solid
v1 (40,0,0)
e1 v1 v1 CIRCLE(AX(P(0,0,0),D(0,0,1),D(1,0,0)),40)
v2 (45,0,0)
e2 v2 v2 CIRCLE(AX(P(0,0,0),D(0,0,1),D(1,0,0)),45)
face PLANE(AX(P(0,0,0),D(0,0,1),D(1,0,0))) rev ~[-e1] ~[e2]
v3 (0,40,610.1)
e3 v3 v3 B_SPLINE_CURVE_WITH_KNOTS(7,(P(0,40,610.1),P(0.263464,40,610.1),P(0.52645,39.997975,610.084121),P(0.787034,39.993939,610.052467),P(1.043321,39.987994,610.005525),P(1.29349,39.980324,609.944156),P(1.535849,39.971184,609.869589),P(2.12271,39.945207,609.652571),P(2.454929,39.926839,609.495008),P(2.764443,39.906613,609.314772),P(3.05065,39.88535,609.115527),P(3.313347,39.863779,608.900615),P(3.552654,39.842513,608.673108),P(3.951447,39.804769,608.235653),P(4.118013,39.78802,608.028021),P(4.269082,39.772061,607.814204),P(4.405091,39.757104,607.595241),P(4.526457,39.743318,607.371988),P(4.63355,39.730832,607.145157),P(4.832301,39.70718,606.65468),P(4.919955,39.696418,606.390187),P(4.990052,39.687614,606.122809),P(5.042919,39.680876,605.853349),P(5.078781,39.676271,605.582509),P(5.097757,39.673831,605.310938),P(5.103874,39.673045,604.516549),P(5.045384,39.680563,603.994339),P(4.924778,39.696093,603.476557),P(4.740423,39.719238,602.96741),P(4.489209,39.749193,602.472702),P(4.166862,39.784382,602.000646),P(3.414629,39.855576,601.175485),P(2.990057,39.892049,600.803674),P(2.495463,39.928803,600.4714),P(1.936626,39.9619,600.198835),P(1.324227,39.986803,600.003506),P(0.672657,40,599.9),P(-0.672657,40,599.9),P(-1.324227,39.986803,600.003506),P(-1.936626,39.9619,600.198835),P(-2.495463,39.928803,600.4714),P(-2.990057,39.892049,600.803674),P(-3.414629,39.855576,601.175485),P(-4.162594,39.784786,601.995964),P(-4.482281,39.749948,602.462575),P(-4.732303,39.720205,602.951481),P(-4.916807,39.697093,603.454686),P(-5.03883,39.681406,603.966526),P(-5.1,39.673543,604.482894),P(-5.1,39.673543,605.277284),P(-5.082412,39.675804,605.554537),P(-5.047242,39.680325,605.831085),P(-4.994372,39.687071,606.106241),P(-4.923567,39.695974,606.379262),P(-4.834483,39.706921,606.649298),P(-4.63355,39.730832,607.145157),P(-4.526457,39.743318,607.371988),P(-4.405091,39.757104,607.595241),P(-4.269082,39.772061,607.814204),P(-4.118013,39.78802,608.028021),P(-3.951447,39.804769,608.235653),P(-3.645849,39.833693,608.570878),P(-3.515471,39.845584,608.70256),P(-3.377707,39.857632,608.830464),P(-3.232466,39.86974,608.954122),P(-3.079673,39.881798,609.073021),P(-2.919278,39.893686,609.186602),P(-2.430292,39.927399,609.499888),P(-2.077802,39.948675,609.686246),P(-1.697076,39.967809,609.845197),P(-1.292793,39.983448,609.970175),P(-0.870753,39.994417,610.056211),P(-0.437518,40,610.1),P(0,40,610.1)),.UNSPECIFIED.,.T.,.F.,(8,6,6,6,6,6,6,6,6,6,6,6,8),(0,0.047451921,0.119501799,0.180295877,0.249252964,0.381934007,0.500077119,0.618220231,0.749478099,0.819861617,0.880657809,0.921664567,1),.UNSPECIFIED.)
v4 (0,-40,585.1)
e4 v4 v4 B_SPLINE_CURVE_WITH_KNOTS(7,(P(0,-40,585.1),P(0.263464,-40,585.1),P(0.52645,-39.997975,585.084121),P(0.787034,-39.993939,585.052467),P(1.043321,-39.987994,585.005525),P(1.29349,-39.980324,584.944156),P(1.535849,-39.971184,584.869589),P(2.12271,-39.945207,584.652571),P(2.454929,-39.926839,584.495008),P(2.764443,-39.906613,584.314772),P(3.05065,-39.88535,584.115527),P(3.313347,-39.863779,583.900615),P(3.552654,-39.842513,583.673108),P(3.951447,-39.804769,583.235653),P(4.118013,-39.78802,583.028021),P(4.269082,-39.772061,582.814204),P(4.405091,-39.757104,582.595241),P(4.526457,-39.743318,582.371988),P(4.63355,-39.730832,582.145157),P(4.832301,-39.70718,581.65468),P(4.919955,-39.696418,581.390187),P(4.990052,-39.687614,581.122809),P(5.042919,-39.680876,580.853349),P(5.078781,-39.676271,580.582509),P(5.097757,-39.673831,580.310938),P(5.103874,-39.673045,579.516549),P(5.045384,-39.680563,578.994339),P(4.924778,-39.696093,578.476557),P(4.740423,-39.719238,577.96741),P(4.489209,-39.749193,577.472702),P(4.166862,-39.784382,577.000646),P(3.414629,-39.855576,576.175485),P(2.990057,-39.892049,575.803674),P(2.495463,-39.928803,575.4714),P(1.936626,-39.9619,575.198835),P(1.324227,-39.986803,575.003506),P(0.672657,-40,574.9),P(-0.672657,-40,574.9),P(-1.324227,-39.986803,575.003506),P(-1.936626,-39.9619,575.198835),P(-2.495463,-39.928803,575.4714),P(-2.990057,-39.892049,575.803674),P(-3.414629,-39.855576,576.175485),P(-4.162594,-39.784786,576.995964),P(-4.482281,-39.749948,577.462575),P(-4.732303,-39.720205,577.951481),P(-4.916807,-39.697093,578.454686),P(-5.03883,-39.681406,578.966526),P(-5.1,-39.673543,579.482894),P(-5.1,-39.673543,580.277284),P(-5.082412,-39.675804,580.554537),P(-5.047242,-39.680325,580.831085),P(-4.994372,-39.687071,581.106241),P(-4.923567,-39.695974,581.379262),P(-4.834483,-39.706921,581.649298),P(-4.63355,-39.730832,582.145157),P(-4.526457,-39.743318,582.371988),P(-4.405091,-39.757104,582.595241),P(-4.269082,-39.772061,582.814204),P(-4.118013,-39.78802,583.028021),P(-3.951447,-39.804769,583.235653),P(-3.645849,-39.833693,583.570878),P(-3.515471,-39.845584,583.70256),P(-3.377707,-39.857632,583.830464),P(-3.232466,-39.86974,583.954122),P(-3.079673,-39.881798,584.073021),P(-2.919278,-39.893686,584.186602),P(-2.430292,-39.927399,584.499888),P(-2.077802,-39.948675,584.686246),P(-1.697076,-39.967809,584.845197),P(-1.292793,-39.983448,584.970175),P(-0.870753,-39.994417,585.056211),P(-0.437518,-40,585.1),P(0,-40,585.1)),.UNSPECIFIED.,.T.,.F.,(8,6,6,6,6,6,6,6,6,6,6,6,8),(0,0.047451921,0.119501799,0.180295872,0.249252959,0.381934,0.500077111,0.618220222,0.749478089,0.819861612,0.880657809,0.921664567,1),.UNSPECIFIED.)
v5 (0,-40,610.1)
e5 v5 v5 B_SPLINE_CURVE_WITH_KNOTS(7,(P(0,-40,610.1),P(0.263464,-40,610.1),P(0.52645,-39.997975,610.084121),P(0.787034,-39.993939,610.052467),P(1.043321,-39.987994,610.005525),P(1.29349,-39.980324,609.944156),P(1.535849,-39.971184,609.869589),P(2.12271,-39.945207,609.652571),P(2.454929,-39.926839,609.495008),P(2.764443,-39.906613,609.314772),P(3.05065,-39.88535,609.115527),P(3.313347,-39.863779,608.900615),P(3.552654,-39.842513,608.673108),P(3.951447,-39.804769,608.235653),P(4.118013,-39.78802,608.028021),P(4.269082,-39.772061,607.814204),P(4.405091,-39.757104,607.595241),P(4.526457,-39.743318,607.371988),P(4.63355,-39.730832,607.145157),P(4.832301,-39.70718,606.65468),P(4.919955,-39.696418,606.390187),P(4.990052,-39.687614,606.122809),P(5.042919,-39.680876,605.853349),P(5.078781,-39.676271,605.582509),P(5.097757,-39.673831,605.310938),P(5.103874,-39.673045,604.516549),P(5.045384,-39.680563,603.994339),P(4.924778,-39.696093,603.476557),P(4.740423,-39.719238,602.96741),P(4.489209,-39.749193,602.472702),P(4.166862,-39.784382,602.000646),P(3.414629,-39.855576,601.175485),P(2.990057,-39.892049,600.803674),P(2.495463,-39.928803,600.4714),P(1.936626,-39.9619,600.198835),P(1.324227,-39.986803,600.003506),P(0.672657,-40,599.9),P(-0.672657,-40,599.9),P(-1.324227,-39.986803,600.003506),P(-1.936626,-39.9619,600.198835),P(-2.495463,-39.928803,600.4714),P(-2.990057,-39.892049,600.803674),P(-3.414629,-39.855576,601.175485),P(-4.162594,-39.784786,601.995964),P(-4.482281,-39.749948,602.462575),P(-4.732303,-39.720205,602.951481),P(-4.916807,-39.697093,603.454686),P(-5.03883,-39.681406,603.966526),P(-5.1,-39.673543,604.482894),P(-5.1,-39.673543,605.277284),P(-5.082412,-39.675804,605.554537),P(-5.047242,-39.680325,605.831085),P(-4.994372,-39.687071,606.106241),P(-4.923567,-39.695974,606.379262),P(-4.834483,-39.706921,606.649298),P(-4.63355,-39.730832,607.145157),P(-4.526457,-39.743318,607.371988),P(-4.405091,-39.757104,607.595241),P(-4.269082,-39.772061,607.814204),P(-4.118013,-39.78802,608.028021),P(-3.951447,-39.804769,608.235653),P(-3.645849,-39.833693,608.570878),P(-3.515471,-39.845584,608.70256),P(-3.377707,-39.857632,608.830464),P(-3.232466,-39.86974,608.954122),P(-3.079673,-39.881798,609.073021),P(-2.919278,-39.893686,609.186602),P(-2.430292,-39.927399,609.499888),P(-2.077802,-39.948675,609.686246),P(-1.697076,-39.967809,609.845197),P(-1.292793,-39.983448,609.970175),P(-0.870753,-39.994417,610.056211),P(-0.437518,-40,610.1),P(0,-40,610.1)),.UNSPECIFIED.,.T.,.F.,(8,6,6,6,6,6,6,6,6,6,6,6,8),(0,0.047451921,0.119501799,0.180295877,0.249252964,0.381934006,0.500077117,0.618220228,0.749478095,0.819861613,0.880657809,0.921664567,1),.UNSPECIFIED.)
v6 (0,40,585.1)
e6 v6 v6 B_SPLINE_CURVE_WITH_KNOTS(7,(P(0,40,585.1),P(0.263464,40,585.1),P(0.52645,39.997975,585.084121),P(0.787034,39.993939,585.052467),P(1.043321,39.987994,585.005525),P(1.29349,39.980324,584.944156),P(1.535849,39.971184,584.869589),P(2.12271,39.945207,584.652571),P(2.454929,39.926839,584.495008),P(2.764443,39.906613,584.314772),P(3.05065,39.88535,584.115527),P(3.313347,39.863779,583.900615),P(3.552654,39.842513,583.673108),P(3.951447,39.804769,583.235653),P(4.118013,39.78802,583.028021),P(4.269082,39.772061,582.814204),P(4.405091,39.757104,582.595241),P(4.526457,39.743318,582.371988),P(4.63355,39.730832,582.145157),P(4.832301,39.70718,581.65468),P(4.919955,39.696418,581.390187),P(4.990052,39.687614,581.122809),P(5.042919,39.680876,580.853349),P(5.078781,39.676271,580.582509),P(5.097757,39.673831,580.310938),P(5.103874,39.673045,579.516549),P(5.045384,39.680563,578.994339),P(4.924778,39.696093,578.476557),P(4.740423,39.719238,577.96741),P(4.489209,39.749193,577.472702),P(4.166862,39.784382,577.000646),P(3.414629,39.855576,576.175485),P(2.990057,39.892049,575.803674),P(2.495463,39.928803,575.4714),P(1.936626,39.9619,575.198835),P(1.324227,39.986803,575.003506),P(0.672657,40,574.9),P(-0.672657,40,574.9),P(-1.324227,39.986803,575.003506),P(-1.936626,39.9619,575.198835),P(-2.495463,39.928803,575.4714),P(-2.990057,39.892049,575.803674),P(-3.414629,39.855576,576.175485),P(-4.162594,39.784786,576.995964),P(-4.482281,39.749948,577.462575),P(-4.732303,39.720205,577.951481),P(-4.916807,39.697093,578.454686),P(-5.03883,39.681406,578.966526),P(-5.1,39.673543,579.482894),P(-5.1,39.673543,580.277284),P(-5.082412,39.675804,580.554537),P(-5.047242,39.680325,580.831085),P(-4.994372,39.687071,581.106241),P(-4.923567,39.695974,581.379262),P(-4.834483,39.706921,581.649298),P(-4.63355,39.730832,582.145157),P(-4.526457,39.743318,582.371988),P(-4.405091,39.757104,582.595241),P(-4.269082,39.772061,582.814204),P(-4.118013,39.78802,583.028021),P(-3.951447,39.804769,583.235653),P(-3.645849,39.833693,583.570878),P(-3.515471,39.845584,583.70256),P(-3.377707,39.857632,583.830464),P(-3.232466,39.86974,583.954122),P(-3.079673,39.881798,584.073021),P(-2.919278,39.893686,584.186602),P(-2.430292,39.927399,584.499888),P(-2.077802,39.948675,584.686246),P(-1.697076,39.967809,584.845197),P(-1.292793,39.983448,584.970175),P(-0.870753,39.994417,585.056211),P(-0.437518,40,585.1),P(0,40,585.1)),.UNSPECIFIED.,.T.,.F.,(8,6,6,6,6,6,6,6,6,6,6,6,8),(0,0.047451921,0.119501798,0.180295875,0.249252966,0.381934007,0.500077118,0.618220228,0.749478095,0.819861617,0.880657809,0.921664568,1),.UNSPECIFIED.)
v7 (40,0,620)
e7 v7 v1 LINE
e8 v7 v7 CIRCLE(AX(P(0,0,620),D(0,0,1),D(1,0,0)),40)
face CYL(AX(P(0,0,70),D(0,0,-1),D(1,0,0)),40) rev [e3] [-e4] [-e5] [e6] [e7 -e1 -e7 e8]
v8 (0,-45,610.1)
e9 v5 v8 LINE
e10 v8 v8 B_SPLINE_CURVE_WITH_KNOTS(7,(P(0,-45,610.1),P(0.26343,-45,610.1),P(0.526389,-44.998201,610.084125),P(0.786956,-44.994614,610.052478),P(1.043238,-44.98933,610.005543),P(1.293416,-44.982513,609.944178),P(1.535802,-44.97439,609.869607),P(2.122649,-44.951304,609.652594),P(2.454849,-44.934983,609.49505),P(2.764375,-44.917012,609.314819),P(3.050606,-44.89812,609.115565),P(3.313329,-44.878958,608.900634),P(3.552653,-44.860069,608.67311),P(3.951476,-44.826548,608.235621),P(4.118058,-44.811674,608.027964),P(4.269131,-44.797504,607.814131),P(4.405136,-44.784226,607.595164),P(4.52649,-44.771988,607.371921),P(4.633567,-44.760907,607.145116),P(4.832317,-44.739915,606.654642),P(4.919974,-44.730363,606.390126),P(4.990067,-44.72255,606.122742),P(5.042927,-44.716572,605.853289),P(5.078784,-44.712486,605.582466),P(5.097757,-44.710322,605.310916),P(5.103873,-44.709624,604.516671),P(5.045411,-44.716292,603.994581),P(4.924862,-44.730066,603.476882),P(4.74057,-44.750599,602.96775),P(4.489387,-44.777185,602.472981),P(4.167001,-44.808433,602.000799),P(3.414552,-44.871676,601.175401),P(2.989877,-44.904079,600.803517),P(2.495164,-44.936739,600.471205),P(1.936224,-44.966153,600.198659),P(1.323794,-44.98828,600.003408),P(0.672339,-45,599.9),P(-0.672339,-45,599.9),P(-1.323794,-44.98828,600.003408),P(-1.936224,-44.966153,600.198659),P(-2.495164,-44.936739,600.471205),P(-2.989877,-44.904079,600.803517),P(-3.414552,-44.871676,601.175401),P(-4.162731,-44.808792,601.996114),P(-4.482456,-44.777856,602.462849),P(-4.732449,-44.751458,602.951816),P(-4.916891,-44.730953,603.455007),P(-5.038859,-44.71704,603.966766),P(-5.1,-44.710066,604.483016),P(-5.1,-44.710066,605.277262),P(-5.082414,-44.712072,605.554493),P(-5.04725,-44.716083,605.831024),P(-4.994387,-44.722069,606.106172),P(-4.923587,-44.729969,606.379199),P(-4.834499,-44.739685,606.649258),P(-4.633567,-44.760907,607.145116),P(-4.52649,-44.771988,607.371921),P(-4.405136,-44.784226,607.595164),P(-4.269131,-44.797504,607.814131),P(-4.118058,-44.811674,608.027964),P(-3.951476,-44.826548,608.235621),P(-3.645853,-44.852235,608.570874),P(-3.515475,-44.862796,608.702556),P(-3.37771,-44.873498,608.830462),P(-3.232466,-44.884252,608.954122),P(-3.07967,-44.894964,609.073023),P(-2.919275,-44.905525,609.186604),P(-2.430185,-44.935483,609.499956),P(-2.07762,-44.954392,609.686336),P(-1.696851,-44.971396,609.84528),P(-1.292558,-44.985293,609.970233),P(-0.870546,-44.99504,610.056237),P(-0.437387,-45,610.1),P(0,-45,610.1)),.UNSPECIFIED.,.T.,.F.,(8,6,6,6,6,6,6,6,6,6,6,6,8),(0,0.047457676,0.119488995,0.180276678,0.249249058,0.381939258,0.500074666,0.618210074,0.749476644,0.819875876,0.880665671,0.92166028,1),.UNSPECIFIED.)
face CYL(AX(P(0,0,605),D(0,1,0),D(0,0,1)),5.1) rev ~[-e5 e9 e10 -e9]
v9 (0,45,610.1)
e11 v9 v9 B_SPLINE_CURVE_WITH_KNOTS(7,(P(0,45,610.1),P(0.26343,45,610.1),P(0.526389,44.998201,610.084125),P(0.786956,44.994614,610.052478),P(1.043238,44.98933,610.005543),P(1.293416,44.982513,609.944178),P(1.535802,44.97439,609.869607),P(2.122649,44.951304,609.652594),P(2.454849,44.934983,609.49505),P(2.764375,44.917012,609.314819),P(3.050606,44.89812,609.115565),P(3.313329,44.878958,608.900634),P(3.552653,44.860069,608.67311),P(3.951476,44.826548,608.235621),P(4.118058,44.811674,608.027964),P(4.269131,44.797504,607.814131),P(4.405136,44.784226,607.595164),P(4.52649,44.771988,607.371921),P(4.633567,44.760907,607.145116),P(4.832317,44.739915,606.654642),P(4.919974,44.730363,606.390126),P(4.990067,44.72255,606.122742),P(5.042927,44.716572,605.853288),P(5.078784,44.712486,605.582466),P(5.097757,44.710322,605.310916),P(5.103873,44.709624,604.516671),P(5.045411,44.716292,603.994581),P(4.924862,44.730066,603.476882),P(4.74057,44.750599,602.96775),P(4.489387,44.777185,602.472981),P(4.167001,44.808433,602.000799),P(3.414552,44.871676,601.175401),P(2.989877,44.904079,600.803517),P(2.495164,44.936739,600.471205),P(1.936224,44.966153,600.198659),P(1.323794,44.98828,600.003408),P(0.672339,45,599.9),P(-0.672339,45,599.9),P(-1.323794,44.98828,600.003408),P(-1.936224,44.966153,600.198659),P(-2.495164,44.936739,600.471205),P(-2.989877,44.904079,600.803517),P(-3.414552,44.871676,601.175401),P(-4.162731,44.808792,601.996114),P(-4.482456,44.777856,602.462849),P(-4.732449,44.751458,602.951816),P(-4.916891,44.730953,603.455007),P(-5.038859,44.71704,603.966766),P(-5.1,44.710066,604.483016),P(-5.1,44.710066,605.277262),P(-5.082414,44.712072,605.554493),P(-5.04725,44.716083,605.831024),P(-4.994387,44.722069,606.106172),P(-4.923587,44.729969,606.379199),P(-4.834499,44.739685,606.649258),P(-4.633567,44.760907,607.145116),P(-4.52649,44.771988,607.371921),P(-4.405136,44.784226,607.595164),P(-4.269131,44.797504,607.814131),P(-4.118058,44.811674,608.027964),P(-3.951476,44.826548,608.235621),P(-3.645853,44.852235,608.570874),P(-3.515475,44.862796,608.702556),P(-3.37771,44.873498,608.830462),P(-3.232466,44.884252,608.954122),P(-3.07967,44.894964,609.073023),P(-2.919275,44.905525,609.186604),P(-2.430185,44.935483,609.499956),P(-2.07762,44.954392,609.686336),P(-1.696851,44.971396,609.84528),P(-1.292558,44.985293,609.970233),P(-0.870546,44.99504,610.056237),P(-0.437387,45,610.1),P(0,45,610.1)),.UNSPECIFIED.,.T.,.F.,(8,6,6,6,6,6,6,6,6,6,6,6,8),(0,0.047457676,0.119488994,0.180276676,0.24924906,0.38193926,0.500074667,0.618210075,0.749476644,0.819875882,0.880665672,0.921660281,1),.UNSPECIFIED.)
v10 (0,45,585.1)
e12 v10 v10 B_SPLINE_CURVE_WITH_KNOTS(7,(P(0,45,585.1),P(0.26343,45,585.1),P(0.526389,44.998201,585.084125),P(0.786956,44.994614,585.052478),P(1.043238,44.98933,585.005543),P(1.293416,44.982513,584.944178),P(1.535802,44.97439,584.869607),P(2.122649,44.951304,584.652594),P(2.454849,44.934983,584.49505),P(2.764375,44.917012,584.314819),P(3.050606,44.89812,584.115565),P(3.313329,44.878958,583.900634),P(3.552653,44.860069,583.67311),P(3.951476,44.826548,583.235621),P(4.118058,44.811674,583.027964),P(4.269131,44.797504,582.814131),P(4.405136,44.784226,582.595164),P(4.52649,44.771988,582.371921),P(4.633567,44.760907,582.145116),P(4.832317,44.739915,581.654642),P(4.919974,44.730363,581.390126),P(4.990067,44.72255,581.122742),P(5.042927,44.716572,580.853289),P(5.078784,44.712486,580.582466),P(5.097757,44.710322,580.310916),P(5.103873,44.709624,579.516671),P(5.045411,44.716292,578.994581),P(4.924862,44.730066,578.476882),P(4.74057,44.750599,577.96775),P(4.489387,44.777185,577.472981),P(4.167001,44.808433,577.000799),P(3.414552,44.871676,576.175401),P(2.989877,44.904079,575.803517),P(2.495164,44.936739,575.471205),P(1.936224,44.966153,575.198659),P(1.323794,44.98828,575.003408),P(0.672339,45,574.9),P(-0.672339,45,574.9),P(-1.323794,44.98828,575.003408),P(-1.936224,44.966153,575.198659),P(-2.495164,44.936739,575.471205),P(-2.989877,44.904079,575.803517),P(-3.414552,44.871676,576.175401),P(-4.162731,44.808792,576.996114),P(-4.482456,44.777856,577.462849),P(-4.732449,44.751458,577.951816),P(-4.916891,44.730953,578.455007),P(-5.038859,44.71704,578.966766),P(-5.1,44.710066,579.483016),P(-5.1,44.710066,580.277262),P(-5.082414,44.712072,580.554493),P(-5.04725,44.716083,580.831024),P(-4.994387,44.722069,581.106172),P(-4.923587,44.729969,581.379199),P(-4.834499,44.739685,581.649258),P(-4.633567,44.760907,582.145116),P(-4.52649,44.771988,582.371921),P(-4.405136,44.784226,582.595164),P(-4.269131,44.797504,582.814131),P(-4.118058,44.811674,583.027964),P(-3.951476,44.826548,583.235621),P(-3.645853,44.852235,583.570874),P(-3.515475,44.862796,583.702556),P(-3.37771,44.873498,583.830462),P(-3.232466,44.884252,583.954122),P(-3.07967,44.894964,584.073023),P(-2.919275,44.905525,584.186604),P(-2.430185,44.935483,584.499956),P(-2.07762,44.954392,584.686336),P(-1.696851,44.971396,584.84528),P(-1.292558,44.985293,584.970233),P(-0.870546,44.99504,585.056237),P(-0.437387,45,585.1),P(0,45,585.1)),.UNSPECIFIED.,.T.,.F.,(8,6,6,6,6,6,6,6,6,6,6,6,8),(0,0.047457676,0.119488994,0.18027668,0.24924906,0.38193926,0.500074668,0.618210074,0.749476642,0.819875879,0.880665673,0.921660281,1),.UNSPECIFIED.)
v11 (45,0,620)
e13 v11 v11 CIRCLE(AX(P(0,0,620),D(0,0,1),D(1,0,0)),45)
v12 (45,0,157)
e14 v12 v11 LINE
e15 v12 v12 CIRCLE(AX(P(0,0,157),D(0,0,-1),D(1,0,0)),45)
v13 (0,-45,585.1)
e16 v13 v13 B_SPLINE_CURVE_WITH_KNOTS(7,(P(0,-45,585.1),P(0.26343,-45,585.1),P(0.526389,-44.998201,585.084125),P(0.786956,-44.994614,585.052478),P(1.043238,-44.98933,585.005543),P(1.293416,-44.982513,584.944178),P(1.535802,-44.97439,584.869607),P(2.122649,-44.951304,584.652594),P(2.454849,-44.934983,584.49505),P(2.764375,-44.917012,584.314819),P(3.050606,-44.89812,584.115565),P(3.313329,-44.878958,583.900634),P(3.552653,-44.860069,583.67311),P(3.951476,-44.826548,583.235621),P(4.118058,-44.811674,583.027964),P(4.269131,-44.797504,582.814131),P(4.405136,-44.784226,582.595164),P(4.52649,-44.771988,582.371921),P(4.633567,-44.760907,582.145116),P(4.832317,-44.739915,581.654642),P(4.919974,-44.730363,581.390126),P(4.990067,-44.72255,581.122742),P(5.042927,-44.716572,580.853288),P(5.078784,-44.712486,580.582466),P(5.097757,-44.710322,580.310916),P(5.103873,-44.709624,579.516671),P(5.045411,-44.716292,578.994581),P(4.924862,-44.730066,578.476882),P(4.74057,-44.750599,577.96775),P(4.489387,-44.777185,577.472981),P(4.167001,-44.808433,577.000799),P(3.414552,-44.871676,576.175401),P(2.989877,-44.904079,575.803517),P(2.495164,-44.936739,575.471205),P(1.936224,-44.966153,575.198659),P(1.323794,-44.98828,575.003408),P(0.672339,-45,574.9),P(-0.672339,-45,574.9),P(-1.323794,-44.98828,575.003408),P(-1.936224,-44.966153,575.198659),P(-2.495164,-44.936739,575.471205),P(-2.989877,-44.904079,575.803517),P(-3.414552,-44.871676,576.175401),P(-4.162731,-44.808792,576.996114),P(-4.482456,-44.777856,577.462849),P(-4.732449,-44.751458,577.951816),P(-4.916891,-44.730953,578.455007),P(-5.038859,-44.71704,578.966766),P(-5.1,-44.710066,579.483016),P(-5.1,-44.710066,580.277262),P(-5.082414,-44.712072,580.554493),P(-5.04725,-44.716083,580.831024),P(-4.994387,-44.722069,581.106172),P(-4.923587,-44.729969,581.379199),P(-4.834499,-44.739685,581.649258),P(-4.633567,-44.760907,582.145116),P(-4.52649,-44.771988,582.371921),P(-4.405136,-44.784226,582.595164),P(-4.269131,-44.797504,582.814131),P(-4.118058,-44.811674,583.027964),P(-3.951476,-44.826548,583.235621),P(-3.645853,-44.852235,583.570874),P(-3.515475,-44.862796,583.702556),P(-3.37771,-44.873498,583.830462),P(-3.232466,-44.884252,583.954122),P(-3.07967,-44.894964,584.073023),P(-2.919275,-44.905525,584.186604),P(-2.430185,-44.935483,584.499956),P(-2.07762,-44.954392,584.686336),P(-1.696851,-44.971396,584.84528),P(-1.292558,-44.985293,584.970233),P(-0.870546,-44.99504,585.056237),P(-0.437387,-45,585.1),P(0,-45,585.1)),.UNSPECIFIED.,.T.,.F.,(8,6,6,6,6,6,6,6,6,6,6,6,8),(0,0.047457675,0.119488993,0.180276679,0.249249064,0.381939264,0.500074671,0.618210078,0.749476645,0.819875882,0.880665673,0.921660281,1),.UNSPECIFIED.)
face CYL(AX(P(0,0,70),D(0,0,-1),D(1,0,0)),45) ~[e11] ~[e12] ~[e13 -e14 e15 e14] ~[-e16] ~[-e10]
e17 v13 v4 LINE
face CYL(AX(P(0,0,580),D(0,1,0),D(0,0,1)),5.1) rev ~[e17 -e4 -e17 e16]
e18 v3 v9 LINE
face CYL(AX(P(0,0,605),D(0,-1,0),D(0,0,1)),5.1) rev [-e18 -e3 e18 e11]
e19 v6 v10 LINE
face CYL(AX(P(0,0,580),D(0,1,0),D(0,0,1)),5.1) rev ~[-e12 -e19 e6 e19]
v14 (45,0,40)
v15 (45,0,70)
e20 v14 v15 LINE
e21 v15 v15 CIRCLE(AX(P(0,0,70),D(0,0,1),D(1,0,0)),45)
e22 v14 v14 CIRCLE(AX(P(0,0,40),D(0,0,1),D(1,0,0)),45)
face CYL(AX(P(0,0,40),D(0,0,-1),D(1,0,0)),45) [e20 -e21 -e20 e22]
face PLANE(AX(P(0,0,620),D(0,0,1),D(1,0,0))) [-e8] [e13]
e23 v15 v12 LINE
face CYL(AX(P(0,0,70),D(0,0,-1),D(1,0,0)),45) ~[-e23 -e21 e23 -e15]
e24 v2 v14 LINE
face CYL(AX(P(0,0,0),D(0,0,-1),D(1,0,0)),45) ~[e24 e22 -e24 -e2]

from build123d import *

# Parameters (mm, degrees)
SKETCH_1_R          = 45
SKETCH_1_R_2        = 40
EXTRUDE_1_DEPTH     = 40
SKETCH_2_R          = 50
SKETCH_2_R_2        = 40
EXTRUDE_2_DEPTH     = 30
SKETCH_3_R          = 45
SKETCH_3_R_2        = 40
EXTRUDE_3_DEPTH     = 550
SKETCH_4_R          = 5.1
CUT_EXTRUDE_1_DEPTH = 91
SKETCH_5_R          = 50
SKETCH_5_R_2        = 45
CUT_EXTRUDE_2_DEPTH = 117


with BuildPart() as part:
    # 草图1 → 凸台-拉伸1 (new body)
    with BuildSketch(Plane.XY):
        Circle(SKETCH_1_R)
        Circle(SKETCH_1_R_2, mode=Mode.SUBTRACT)
    extrude(amount=EXTRUDE_1_DEPTH)

    # 草图2 → 凸台-拉伸2 (add)
    with BuildSketch(Plane.XY.offset(40)):
        Circle(SKETCH_2_R)
        Circle(SKETCH_2_R_2, mode=Mode.SUBTRACT)
    extrude(amount=EXTRUDE_2_DEPTH)

    # 草图3 → 凸台-拉伸3 (add)
    with BuildSketch(Plane.XY.offset(70)):
        Circle(SKETCH_3_R)
        Circle(SKETCH_3_R_2, mode=Mode.SUBTRACT)
    extrude(amount=EXTRUDE_3_DEPTH)

    # 草图4 → 切除-拉伸1 (cut, symmetric)
    with BuildSketch(Plane(origin=(0, 0, 0), x_dir=(1, 0, 0), z_dir=(0, 1, 0))):
        with Locations(Location((0, -605, 0), (0, 0, 270))):
            Circle(SKETCH_4_R)
        with Locations(Location((0, -580, 0), (0, 0, 270))):
            Circle(SKETCH_4_R)
    extrude(amount=CUT_EXTRUDE_1_DEPTH, both=True, mode=Mode.SUBTRACT)

    # 草图5 → 切除-拉伸2 (cut)
    with BuildSketch(Plane(origin=(0, 0, 40), x_dir=(-1, 0, 0), z_dir=(0, 0, -1))):
        Circle(SKETCH_5_R)
        with Locations(Location((0, 0, 0), (0, 0, 180))):
            Circle(SKETCH_5_R_2, mode=Mode.SUBTRACT)
    extrude(amount=-CUT_EXTRUDE_2_DEPTH, mode=Mode.SUBTRACT)


solid = part.part
